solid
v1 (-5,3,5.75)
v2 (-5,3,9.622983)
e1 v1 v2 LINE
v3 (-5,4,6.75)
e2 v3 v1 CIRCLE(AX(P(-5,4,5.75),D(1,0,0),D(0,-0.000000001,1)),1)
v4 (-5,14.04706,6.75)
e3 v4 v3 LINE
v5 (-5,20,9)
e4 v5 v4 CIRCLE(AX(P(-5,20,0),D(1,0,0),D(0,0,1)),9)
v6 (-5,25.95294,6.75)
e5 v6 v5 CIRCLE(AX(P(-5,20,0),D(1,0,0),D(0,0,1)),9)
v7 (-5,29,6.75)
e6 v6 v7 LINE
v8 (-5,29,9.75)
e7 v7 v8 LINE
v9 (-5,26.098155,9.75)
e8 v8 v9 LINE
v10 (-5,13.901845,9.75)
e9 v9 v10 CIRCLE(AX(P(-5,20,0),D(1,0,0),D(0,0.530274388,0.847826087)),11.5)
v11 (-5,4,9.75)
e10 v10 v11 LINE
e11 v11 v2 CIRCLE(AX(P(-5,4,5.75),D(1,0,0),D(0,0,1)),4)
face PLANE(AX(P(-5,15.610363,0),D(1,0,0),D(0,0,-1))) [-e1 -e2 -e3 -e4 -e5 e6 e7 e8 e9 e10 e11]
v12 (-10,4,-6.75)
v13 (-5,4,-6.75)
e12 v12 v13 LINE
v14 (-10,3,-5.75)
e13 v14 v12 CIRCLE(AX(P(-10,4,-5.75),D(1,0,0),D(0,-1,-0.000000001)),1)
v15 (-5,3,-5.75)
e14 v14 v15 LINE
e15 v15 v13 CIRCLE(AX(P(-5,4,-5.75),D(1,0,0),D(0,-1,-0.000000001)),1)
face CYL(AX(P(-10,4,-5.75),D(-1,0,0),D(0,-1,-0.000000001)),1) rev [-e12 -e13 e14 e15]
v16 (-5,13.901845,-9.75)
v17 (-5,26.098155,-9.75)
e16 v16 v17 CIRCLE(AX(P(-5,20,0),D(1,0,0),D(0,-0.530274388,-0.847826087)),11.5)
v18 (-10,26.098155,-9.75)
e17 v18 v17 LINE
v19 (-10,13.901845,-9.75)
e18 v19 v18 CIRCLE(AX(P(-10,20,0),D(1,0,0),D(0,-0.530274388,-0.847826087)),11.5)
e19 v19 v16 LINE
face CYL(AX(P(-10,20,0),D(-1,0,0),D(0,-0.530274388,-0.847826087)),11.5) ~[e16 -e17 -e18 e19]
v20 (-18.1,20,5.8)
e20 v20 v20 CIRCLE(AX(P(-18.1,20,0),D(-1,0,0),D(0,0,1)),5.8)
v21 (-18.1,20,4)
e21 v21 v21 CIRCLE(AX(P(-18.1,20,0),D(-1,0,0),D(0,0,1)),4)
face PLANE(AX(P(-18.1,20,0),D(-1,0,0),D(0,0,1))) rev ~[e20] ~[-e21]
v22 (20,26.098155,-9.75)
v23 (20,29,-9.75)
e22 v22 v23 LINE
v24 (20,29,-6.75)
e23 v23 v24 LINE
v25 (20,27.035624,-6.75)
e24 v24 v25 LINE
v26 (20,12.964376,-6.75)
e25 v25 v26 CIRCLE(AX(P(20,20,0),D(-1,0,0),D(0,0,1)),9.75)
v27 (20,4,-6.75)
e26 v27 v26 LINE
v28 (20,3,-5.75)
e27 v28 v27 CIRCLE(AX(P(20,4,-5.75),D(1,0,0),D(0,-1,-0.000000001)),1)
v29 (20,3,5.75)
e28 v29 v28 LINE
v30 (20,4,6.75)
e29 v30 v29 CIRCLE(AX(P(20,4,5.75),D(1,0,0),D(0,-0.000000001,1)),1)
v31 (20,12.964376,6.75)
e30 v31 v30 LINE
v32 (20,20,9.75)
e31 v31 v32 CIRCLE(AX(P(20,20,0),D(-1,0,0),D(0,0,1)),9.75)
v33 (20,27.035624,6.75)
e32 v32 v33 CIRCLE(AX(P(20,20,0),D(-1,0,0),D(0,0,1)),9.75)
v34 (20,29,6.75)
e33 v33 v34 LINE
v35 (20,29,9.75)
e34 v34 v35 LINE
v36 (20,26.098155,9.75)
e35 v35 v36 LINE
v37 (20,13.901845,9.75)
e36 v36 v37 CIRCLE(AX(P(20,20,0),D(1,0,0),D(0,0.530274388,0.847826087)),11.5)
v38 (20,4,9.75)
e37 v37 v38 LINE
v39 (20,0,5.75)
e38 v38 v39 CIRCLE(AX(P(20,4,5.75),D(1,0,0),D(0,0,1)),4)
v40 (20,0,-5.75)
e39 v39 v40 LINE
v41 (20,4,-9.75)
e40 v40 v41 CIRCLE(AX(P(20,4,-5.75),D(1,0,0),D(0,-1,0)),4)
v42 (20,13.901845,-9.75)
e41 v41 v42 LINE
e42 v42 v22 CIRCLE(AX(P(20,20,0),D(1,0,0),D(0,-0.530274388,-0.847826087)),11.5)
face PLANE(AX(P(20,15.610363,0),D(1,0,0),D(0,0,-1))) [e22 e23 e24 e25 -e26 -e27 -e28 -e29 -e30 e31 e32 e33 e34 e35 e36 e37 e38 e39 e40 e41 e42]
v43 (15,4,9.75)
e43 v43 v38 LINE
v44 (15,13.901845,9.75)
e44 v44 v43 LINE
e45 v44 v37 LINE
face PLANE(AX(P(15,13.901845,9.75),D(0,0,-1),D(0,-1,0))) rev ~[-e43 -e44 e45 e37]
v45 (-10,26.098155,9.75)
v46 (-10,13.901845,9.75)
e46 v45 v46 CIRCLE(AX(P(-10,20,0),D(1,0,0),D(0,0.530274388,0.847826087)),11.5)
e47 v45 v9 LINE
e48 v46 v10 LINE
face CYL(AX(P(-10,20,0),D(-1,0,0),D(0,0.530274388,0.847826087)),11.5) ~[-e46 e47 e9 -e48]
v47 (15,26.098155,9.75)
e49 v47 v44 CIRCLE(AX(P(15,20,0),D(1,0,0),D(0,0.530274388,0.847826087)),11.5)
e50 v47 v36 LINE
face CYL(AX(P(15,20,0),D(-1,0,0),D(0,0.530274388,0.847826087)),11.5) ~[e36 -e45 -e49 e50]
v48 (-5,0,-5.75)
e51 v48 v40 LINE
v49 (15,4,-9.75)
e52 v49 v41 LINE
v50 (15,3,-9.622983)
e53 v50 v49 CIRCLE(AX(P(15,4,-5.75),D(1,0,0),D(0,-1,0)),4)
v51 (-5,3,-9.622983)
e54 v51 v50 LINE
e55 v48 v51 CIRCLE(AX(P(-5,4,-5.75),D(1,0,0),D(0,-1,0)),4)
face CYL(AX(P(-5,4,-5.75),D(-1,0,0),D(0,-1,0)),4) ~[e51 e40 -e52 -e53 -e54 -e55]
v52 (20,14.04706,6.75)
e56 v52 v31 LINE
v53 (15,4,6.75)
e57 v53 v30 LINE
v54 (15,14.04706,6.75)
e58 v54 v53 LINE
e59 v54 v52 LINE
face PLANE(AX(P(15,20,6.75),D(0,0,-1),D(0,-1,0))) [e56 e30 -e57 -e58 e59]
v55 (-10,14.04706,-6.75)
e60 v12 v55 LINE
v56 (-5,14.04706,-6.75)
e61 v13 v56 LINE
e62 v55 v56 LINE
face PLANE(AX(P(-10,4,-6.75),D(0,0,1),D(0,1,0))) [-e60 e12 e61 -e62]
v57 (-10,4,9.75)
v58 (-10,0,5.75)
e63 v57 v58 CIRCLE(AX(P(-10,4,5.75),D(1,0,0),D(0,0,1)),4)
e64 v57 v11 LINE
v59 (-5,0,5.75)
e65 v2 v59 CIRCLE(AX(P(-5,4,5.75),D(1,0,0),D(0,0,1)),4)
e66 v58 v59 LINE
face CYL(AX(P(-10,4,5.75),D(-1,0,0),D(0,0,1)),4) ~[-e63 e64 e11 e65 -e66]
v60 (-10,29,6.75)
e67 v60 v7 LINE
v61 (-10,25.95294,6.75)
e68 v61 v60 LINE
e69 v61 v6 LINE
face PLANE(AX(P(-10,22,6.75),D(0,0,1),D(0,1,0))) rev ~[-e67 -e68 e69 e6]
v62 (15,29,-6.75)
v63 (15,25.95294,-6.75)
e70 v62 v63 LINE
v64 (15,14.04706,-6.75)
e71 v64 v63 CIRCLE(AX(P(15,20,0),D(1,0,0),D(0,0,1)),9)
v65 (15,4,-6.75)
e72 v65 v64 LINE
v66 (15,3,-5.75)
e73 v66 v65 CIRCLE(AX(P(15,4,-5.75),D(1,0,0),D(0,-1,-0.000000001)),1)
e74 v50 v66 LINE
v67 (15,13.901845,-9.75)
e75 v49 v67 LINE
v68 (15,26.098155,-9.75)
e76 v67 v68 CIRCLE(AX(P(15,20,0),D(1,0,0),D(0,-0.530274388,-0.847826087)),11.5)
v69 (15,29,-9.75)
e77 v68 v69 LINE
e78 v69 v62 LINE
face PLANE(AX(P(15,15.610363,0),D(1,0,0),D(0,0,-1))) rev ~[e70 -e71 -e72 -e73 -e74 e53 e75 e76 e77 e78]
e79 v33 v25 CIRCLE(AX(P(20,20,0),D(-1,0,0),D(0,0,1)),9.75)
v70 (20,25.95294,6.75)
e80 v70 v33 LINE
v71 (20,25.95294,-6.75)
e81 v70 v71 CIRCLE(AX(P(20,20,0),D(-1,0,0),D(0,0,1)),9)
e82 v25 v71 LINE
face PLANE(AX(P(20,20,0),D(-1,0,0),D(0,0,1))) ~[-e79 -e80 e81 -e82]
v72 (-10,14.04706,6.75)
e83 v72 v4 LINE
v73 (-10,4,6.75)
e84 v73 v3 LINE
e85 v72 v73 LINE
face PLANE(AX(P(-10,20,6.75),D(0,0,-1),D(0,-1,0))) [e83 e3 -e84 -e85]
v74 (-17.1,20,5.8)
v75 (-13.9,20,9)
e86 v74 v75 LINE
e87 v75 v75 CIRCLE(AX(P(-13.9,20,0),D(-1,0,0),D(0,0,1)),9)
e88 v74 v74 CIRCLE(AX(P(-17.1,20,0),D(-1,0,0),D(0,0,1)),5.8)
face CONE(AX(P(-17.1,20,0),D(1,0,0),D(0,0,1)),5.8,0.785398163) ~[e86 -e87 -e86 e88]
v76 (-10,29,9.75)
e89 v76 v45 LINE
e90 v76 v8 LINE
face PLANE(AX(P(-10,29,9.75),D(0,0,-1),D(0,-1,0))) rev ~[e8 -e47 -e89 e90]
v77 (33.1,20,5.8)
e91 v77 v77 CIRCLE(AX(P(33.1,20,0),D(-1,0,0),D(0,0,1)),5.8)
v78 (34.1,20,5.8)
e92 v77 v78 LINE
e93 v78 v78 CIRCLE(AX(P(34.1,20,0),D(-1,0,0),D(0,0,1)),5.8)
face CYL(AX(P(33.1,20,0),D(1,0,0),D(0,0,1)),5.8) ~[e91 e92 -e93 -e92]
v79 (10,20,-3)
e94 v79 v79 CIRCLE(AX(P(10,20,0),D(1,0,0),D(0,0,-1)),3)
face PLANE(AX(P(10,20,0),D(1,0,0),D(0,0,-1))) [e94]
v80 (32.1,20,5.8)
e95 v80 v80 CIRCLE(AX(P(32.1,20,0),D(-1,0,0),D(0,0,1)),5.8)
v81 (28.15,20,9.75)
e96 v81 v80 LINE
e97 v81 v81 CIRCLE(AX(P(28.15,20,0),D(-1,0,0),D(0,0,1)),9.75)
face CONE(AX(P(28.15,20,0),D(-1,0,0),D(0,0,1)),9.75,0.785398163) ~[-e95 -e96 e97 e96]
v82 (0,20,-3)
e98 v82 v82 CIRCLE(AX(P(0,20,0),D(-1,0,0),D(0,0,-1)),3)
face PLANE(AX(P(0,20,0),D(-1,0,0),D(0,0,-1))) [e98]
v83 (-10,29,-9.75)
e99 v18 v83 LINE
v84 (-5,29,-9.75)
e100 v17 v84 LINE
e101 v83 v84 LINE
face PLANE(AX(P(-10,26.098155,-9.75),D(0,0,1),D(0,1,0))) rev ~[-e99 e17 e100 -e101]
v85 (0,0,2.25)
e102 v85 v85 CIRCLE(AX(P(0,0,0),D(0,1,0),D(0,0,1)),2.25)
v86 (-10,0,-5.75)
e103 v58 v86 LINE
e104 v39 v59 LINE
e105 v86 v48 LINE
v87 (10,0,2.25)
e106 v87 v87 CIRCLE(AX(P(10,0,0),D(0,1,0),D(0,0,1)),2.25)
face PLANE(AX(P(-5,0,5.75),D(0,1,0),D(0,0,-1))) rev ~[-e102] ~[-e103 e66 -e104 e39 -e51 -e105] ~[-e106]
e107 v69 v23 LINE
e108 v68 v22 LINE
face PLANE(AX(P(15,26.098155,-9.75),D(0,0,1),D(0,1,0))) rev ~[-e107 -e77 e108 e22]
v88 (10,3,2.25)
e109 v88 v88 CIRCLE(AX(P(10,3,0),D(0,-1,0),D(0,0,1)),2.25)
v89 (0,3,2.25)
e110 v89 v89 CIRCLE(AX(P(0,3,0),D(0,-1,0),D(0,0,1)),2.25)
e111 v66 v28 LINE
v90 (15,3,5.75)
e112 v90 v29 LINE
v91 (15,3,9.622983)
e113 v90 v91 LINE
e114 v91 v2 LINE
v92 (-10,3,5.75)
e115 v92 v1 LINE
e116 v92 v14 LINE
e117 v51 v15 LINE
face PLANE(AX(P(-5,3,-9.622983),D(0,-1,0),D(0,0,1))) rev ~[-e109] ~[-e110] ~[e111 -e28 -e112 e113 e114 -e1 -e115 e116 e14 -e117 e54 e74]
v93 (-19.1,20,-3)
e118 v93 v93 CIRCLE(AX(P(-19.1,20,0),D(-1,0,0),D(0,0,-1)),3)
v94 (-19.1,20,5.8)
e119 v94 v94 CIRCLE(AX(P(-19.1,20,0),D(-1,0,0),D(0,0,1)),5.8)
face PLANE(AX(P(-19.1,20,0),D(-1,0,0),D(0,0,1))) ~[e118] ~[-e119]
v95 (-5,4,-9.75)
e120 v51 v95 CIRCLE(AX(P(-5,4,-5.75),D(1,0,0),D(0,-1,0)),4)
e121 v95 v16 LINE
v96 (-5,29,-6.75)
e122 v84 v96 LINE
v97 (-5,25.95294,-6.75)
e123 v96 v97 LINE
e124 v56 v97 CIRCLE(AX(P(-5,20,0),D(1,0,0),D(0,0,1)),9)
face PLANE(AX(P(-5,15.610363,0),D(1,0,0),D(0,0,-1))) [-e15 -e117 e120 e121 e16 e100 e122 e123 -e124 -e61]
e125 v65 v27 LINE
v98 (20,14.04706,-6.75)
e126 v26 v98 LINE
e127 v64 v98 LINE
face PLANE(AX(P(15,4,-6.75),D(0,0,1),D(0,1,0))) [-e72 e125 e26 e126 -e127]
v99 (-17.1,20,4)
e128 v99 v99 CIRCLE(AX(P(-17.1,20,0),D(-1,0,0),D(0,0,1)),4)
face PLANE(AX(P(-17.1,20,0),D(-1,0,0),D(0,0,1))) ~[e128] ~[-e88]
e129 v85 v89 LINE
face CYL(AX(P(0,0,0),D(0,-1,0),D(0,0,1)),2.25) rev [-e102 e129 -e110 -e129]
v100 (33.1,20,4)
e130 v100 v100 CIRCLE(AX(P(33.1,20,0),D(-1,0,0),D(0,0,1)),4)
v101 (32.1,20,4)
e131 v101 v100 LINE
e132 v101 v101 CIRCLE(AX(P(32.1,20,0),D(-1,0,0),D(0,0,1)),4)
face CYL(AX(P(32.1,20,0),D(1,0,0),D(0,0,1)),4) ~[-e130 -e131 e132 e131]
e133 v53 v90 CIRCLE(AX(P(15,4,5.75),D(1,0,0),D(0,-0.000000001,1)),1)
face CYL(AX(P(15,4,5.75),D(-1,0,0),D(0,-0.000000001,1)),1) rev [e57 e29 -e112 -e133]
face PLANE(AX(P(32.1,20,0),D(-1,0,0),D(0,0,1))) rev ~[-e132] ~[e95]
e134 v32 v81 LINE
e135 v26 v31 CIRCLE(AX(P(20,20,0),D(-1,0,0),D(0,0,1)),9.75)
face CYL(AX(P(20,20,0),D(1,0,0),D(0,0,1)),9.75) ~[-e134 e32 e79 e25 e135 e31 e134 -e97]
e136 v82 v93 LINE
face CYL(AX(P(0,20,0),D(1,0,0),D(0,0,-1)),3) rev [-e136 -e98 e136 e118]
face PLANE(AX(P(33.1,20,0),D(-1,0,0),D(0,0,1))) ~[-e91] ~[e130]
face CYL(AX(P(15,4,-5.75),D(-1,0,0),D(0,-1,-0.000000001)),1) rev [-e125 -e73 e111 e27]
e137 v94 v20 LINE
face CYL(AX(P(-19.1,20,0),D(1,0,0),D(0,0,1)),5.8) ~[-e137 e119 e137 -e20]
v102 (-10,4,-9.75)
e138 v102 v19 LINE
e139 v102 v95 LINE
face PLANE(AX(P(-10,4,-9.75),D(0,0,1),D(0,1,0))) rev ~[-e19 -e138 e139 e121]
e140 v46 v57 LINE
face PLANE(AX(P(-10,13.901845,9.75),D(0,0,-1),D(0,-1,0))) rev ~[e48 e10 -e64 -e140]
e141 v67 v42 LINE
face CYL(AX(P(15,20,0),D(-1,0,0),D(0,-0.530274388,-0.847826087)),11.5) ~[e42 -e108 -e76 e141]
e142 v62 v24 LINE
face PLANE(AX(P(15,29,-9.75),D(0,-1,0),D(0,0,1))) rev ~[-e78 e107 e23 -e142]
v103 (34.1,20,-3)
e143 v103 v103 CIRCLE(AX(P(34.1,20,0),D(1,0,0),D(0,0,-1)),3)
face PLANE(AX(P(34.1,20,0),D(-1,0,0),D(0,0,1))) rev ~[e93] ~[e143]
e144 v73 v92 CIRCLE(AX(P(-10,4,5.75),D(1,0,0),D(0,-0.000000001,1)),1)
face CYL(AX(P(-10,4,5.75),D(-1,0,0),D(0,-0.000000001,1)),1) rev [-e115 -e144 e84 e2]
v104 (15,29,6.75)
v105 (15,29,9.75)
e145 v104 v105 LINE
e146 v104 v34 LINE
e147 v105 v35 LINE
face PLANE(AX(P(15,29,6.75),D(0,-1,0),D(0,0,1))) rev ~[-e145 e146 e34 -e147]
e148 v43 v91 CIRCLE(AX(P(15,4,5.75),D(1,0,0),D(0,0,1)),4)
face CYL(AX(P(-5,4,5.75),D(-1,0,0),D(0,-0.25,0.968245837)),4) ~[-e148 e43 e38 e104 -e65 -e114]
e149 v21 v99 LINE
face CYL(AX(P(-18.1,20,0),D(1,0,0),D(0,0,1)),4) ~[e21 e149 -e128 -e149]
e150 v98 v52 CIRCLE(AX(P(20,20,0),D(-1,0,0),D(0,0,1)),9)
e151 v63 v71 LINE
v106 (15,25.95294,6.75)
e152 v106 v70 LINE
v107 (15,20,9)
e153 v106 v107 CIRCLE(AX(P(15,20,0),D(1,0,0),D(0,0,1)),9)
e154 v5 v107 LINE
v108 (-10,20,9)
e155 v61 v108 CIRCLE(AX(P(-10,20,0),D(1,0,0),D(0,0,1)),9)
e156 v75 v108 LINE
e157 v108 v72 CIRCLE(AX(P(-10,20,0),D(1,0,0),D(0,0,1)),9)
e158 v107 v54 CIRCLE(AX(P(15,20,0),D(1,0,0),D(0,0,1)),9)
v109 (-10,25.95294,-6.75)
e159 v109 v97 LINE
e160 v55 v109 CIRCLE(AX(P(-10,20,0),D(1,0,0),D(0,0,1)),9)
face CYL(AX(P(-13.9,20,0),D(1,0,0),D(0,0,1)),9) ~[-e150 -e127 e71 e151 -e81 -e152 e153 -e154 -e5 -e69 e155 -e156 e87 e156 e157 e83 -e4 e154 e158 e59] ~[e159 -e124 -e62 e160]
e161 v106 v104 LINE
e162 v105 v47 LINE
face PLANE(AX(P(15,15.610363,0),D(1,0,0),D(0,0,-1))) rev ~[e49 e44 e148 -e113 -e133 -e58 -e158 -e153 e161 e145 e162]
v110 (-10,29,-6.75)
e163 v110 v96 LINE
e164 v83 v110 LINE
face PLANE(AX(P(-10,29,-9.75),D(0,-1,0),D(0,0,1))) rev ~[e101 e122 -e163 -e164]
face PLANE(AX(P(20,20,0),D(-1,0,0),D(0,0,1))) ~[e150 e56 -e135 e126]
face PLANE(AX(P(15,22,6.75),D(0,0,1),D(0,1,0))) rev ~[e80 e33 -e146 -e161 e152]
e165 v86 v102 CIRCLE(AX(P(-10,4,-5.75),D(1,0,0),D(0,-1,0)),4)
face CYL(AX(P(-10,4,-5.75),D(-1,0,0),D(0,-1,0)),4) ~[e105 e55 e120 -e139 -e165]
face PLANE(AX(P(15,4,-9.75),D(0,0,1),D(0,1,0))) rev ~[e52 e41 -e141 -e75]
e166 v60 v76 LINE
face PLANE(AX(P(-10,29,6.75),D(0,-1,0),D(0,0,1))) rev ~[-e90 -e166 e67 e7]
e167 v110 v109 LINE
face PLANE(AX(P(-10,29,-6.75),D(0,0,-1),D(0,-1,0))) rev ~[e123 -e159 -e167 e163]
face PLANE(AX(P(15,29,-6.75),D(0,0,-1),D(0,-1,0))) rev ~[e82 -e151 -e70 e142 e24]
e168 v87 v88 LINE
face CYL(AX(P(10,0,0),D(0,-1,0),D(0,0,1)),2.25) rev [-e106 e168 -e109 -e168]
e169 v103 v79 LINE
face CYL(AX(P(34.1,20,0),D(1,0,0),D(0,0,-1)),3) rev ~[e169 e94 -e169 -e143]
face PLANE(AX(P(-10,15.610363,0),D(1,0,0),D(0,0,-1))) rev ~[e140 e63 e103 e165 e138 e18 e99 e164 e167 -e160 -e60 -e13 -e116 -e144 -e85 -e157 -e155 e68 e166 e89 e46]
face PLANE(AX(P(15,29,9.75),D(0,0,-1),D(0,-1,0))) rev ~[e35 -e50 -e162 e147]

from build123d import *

# Parameters (mm, degrees)
EXTRUDE_1_DEPTH     = 5
EXTRUDE_START       = -5
EXTRUDE_2_DEPTH     = 5
EXTRUDE_3_DEPTH     = 15
EXTRUDE_4_DEPTH     = 5
SKETCH_6_R          = 2.25
CUT_EXTRUDE_1_DEPTH = 4
SKETCH_7_R          = 2.25
CUT_EXTRUDE_2_DEPTH = 4
SKETCH_8_R          = 3
CUT_EXTRUDE_3_DEPTH = 24.1
CUT_EXTRUDE_START   = -19.1
SKETCH_9_R          = 3
CUT_EXTRUDE_4_DEPTH = 19.1


with BuildPart() as part:
    # 草图1 → 旋转1 (revolve)
    with BuildSketch(Plane.XY, mode=Mode.PRIVATE) as revolve_1_sk:
        Polygon((-19.1, 20), (-19.1, 25.8), (-18.1, 25.8), (-18.1, 24), (-17.1, 24), (-17.1, 25.8), (-13.9, 29), (20, 29), (20, 29.75), (28.15, 29.75), (32.1, 25.8), (32.1, 24), (33.1, 24), (33.1, 25.8), (34.1, 25.8), (34.1, 20), align=None)
    revolve(revolve_1_sk.sketch.rotate(Axis((34.1, 20, 0), (-1, 0, 0)), 270), axis=Axis((34.1, 20, 0), (-1, 0, 0)))

    # 草图2 → 凸台-拉伸1 (add)
    with BuildSketch(Plane(origin=(-10, 0, 0), x_dir=(0, 0, -1), z_dir=(1, 0, 0))):
        with BuildLine():
            Line((-9.75, 13.901844541), (-9.75, 4))
            ThreePointArc((-9.75, 4), (-8.578427125, 1.171572875), (-5.75, 0))
            Line((-5.75, 0), (5.75, 0))
            ThreePointArc((5.75, 0), (8.578427125, 1.171572875), (9.75, 4))
            Line((9.75, 4), (9.75, 13.901844541))
            ThreePointArc((9.75, 13.901844541), (11.5, 20), (9.75, 26.098155459))
            Line((9.75, 26.098155459), (9.75, 29))
            Line((9.75, 29), (6.75, 29))
            Line((6.75, 29), (6.75, 22))
            Line((6.75, 22), (-6.75, 22))
            Line((-6.75, 22), (-6.75, 29))
            Line((-6.75, 29), (-9.75, 29))
            Line((-9.75, 29), (-9.75, 26.098155459))
            ThreePointArc((-9.75, 26.098155459), (-11.5, 20), (-9.75, 13.901844541))
        make_face()
        with BuildLine():
            Line((-5.75, 3), (5.75, 3))
            ThreePointArc((5.75, 3), (6.457106781, 3.292893219), (6.75, 4))
            Line((6.75, 4), (6.75, 20))
            Line((6.75, 20), (-6.75, 20))
            Line((-6.75, 20), (-6.75, 4))
            ThreePointArc((-6.75, 4), (-6.457106781, 3.292893219), (-5.75, 3))
        make_face(mode=Mode.SUBTRACT)
    extrude(amount=EXTRUDE_1_DEPTH)

    # 草图3 → 凸台-拉伸2 (add)
    with BuildSketch(Plane(origin=(20, 0, 0), x_dir=(0, 0, -1), z_dir=(1, 0, 0)).offset(EXTRUDE_START)):
        with BuildLine():
            Line((-9.75, 13.901844541), (-9.75, 4))
            ThreePointArc((-9.75, 4), (-8.578427125, 1.171572875), (-5.75, 0))
            Line((-5.75, 0), (5.75, 0))
            ThreePointArc((5.75, 0), (8.578427125, 1.171572875), (9.75, 4))
            Line((9.75, 4), (9.75, 13.901844541))
            ThreePointArc((9.75, 13.901844541), (11.5, 20), (9.75, 26.098155459))
            Line((9.75, 26.098155459), (9.75, 29))
            Line((9.75, 29), (6.75, 29))
            Line((6.75, 29), (6.75, 22))
            Line((6.75, 22), (-6.75, 22))
            Line((-6.75, 22), (-6.75, 29))
            Line((-6.75, 29), (-9.75, 29))
            Line((-9.75, 29), (-9.75, 26.098155459))
            ThreePointArc((-9.75, 26.098155459), (-11.5, 20), (-9.75, 13.901844541))
        make_face()
        with BuildLine():
            Line((-5.75, 3), (5.75, 3))
            ThreePointArc((5.75, 3), (6.457106781, 3.292893219), (6.75, 4))
            Line((6.75, 4), (6.75, 20))
            Line((6.75, 20), (-6.75, 20))
            Line((-6.75, 20), (-6.75, 4))
            ThreePointArc((-6.75, 4), (-6.457106781, 3.292893219), (-5.75, 3))
        make_face(mode=Mode.SUBTRACT)
    extrude(amount=EXTRUDE_2_DEPTH)

    # 草图4 → 凸台-拉伸3 (add)
    with BuildSketch(Plane(origin=(0, 0, 0), x_dir=(0, 0, -1), z_dir=(1, 0, 0))):
        with BuildLine():
            Line((-5.75, 0), (5.75, 0))
            ThreePointArc((5.75, 0), (8.199489743, 0.83772234), (9.622983346, 3))
            Line((9.622983346, 3), (-9.622983346, 3))
            ThreePointArc((-9.622983346, 3), (-8.199489743, 0.83772234), (-5.75, 0))
        make_face()
    extrude(amount=EXTRUDE_3_DEPTH)

    # 草图5 → 凸台-拉伸4 (add)
    with BuildSketch(Plane(origin=(0, 0, 0), x_dir=(0, 0, -1), z_dir=(1, 0, 0)).offset(EXTRUDE_START)):
        with BuildLine():
            Line((-5.75, 0), (5.75, 0))
            ThreePointArc((5.75, 0), (8.199489743, 0.83772234), (9.622983346, 3))
            Line((9.622983346, 3), (-9.622983346, 3))
            ThreePointArc((-9.622983346, 3), (-8.199489743, 0.83772234), (-5.75, 0))
        make_face()
    extrude(amount=EXTRUDE_4_DEPTH)

    # 草图6 → 切除-拉伸1 (cut)
    with BuildSketch(Plane(origin=(0, 0, 0), x_dir=(1, 0, 0), z_dir=(0, 1, 0))):
        with Locations(Location((0, 0, 0), (0, 0, 270))):
            Circle(SKETCH_6_R)
    extrude(amount=CUT_EXTRUDE_1_DEPTH, mode=Mode.SUBTRACT)

    # 草图7 → 切除-拉伸2 (cut)
    with BuildSketch(Plane(origin=(0, 0, 0), x_dir=(1, 0, 0), z_dir=(0, 1, 0))):
        with Locations(Location((10, 0, 0), (0, 0, 270))):
            Circle(SKETCH_7_R)
    extrude(amount=CUT_EXTRUDE_2_DEPTH, mode=Mode.SUBTRACT)

    # 草图8 → 切除-拉伸3 (cut)
    with BuildSketch(Plane(origin=(34.1, 0, 0), x_dir=(0, 0, -1), z_dir=(1, 0, 0))):
        with Locations((0, 20)):
            Circle(SKETCH_8_R)
    extrude(amount=-CUT_EXTRUDE_3_DEPTH, mode=Mode.SUBTRACT)

    # 草图9 → 切除-拉伸4 (cut)
    with BuildSketch(Plane.ZY.offset(19.1).offset(CUT_EXTRUDE_START)):
        with Locations(Location((0, 20, 0), (0, 0, 180))):
            Circle(SKETCH_9_R)
    extrude(amount=CUT_EXTRUDE_4_DEPTH, mode=Mode.SUBTRACT)


solid = part.part
